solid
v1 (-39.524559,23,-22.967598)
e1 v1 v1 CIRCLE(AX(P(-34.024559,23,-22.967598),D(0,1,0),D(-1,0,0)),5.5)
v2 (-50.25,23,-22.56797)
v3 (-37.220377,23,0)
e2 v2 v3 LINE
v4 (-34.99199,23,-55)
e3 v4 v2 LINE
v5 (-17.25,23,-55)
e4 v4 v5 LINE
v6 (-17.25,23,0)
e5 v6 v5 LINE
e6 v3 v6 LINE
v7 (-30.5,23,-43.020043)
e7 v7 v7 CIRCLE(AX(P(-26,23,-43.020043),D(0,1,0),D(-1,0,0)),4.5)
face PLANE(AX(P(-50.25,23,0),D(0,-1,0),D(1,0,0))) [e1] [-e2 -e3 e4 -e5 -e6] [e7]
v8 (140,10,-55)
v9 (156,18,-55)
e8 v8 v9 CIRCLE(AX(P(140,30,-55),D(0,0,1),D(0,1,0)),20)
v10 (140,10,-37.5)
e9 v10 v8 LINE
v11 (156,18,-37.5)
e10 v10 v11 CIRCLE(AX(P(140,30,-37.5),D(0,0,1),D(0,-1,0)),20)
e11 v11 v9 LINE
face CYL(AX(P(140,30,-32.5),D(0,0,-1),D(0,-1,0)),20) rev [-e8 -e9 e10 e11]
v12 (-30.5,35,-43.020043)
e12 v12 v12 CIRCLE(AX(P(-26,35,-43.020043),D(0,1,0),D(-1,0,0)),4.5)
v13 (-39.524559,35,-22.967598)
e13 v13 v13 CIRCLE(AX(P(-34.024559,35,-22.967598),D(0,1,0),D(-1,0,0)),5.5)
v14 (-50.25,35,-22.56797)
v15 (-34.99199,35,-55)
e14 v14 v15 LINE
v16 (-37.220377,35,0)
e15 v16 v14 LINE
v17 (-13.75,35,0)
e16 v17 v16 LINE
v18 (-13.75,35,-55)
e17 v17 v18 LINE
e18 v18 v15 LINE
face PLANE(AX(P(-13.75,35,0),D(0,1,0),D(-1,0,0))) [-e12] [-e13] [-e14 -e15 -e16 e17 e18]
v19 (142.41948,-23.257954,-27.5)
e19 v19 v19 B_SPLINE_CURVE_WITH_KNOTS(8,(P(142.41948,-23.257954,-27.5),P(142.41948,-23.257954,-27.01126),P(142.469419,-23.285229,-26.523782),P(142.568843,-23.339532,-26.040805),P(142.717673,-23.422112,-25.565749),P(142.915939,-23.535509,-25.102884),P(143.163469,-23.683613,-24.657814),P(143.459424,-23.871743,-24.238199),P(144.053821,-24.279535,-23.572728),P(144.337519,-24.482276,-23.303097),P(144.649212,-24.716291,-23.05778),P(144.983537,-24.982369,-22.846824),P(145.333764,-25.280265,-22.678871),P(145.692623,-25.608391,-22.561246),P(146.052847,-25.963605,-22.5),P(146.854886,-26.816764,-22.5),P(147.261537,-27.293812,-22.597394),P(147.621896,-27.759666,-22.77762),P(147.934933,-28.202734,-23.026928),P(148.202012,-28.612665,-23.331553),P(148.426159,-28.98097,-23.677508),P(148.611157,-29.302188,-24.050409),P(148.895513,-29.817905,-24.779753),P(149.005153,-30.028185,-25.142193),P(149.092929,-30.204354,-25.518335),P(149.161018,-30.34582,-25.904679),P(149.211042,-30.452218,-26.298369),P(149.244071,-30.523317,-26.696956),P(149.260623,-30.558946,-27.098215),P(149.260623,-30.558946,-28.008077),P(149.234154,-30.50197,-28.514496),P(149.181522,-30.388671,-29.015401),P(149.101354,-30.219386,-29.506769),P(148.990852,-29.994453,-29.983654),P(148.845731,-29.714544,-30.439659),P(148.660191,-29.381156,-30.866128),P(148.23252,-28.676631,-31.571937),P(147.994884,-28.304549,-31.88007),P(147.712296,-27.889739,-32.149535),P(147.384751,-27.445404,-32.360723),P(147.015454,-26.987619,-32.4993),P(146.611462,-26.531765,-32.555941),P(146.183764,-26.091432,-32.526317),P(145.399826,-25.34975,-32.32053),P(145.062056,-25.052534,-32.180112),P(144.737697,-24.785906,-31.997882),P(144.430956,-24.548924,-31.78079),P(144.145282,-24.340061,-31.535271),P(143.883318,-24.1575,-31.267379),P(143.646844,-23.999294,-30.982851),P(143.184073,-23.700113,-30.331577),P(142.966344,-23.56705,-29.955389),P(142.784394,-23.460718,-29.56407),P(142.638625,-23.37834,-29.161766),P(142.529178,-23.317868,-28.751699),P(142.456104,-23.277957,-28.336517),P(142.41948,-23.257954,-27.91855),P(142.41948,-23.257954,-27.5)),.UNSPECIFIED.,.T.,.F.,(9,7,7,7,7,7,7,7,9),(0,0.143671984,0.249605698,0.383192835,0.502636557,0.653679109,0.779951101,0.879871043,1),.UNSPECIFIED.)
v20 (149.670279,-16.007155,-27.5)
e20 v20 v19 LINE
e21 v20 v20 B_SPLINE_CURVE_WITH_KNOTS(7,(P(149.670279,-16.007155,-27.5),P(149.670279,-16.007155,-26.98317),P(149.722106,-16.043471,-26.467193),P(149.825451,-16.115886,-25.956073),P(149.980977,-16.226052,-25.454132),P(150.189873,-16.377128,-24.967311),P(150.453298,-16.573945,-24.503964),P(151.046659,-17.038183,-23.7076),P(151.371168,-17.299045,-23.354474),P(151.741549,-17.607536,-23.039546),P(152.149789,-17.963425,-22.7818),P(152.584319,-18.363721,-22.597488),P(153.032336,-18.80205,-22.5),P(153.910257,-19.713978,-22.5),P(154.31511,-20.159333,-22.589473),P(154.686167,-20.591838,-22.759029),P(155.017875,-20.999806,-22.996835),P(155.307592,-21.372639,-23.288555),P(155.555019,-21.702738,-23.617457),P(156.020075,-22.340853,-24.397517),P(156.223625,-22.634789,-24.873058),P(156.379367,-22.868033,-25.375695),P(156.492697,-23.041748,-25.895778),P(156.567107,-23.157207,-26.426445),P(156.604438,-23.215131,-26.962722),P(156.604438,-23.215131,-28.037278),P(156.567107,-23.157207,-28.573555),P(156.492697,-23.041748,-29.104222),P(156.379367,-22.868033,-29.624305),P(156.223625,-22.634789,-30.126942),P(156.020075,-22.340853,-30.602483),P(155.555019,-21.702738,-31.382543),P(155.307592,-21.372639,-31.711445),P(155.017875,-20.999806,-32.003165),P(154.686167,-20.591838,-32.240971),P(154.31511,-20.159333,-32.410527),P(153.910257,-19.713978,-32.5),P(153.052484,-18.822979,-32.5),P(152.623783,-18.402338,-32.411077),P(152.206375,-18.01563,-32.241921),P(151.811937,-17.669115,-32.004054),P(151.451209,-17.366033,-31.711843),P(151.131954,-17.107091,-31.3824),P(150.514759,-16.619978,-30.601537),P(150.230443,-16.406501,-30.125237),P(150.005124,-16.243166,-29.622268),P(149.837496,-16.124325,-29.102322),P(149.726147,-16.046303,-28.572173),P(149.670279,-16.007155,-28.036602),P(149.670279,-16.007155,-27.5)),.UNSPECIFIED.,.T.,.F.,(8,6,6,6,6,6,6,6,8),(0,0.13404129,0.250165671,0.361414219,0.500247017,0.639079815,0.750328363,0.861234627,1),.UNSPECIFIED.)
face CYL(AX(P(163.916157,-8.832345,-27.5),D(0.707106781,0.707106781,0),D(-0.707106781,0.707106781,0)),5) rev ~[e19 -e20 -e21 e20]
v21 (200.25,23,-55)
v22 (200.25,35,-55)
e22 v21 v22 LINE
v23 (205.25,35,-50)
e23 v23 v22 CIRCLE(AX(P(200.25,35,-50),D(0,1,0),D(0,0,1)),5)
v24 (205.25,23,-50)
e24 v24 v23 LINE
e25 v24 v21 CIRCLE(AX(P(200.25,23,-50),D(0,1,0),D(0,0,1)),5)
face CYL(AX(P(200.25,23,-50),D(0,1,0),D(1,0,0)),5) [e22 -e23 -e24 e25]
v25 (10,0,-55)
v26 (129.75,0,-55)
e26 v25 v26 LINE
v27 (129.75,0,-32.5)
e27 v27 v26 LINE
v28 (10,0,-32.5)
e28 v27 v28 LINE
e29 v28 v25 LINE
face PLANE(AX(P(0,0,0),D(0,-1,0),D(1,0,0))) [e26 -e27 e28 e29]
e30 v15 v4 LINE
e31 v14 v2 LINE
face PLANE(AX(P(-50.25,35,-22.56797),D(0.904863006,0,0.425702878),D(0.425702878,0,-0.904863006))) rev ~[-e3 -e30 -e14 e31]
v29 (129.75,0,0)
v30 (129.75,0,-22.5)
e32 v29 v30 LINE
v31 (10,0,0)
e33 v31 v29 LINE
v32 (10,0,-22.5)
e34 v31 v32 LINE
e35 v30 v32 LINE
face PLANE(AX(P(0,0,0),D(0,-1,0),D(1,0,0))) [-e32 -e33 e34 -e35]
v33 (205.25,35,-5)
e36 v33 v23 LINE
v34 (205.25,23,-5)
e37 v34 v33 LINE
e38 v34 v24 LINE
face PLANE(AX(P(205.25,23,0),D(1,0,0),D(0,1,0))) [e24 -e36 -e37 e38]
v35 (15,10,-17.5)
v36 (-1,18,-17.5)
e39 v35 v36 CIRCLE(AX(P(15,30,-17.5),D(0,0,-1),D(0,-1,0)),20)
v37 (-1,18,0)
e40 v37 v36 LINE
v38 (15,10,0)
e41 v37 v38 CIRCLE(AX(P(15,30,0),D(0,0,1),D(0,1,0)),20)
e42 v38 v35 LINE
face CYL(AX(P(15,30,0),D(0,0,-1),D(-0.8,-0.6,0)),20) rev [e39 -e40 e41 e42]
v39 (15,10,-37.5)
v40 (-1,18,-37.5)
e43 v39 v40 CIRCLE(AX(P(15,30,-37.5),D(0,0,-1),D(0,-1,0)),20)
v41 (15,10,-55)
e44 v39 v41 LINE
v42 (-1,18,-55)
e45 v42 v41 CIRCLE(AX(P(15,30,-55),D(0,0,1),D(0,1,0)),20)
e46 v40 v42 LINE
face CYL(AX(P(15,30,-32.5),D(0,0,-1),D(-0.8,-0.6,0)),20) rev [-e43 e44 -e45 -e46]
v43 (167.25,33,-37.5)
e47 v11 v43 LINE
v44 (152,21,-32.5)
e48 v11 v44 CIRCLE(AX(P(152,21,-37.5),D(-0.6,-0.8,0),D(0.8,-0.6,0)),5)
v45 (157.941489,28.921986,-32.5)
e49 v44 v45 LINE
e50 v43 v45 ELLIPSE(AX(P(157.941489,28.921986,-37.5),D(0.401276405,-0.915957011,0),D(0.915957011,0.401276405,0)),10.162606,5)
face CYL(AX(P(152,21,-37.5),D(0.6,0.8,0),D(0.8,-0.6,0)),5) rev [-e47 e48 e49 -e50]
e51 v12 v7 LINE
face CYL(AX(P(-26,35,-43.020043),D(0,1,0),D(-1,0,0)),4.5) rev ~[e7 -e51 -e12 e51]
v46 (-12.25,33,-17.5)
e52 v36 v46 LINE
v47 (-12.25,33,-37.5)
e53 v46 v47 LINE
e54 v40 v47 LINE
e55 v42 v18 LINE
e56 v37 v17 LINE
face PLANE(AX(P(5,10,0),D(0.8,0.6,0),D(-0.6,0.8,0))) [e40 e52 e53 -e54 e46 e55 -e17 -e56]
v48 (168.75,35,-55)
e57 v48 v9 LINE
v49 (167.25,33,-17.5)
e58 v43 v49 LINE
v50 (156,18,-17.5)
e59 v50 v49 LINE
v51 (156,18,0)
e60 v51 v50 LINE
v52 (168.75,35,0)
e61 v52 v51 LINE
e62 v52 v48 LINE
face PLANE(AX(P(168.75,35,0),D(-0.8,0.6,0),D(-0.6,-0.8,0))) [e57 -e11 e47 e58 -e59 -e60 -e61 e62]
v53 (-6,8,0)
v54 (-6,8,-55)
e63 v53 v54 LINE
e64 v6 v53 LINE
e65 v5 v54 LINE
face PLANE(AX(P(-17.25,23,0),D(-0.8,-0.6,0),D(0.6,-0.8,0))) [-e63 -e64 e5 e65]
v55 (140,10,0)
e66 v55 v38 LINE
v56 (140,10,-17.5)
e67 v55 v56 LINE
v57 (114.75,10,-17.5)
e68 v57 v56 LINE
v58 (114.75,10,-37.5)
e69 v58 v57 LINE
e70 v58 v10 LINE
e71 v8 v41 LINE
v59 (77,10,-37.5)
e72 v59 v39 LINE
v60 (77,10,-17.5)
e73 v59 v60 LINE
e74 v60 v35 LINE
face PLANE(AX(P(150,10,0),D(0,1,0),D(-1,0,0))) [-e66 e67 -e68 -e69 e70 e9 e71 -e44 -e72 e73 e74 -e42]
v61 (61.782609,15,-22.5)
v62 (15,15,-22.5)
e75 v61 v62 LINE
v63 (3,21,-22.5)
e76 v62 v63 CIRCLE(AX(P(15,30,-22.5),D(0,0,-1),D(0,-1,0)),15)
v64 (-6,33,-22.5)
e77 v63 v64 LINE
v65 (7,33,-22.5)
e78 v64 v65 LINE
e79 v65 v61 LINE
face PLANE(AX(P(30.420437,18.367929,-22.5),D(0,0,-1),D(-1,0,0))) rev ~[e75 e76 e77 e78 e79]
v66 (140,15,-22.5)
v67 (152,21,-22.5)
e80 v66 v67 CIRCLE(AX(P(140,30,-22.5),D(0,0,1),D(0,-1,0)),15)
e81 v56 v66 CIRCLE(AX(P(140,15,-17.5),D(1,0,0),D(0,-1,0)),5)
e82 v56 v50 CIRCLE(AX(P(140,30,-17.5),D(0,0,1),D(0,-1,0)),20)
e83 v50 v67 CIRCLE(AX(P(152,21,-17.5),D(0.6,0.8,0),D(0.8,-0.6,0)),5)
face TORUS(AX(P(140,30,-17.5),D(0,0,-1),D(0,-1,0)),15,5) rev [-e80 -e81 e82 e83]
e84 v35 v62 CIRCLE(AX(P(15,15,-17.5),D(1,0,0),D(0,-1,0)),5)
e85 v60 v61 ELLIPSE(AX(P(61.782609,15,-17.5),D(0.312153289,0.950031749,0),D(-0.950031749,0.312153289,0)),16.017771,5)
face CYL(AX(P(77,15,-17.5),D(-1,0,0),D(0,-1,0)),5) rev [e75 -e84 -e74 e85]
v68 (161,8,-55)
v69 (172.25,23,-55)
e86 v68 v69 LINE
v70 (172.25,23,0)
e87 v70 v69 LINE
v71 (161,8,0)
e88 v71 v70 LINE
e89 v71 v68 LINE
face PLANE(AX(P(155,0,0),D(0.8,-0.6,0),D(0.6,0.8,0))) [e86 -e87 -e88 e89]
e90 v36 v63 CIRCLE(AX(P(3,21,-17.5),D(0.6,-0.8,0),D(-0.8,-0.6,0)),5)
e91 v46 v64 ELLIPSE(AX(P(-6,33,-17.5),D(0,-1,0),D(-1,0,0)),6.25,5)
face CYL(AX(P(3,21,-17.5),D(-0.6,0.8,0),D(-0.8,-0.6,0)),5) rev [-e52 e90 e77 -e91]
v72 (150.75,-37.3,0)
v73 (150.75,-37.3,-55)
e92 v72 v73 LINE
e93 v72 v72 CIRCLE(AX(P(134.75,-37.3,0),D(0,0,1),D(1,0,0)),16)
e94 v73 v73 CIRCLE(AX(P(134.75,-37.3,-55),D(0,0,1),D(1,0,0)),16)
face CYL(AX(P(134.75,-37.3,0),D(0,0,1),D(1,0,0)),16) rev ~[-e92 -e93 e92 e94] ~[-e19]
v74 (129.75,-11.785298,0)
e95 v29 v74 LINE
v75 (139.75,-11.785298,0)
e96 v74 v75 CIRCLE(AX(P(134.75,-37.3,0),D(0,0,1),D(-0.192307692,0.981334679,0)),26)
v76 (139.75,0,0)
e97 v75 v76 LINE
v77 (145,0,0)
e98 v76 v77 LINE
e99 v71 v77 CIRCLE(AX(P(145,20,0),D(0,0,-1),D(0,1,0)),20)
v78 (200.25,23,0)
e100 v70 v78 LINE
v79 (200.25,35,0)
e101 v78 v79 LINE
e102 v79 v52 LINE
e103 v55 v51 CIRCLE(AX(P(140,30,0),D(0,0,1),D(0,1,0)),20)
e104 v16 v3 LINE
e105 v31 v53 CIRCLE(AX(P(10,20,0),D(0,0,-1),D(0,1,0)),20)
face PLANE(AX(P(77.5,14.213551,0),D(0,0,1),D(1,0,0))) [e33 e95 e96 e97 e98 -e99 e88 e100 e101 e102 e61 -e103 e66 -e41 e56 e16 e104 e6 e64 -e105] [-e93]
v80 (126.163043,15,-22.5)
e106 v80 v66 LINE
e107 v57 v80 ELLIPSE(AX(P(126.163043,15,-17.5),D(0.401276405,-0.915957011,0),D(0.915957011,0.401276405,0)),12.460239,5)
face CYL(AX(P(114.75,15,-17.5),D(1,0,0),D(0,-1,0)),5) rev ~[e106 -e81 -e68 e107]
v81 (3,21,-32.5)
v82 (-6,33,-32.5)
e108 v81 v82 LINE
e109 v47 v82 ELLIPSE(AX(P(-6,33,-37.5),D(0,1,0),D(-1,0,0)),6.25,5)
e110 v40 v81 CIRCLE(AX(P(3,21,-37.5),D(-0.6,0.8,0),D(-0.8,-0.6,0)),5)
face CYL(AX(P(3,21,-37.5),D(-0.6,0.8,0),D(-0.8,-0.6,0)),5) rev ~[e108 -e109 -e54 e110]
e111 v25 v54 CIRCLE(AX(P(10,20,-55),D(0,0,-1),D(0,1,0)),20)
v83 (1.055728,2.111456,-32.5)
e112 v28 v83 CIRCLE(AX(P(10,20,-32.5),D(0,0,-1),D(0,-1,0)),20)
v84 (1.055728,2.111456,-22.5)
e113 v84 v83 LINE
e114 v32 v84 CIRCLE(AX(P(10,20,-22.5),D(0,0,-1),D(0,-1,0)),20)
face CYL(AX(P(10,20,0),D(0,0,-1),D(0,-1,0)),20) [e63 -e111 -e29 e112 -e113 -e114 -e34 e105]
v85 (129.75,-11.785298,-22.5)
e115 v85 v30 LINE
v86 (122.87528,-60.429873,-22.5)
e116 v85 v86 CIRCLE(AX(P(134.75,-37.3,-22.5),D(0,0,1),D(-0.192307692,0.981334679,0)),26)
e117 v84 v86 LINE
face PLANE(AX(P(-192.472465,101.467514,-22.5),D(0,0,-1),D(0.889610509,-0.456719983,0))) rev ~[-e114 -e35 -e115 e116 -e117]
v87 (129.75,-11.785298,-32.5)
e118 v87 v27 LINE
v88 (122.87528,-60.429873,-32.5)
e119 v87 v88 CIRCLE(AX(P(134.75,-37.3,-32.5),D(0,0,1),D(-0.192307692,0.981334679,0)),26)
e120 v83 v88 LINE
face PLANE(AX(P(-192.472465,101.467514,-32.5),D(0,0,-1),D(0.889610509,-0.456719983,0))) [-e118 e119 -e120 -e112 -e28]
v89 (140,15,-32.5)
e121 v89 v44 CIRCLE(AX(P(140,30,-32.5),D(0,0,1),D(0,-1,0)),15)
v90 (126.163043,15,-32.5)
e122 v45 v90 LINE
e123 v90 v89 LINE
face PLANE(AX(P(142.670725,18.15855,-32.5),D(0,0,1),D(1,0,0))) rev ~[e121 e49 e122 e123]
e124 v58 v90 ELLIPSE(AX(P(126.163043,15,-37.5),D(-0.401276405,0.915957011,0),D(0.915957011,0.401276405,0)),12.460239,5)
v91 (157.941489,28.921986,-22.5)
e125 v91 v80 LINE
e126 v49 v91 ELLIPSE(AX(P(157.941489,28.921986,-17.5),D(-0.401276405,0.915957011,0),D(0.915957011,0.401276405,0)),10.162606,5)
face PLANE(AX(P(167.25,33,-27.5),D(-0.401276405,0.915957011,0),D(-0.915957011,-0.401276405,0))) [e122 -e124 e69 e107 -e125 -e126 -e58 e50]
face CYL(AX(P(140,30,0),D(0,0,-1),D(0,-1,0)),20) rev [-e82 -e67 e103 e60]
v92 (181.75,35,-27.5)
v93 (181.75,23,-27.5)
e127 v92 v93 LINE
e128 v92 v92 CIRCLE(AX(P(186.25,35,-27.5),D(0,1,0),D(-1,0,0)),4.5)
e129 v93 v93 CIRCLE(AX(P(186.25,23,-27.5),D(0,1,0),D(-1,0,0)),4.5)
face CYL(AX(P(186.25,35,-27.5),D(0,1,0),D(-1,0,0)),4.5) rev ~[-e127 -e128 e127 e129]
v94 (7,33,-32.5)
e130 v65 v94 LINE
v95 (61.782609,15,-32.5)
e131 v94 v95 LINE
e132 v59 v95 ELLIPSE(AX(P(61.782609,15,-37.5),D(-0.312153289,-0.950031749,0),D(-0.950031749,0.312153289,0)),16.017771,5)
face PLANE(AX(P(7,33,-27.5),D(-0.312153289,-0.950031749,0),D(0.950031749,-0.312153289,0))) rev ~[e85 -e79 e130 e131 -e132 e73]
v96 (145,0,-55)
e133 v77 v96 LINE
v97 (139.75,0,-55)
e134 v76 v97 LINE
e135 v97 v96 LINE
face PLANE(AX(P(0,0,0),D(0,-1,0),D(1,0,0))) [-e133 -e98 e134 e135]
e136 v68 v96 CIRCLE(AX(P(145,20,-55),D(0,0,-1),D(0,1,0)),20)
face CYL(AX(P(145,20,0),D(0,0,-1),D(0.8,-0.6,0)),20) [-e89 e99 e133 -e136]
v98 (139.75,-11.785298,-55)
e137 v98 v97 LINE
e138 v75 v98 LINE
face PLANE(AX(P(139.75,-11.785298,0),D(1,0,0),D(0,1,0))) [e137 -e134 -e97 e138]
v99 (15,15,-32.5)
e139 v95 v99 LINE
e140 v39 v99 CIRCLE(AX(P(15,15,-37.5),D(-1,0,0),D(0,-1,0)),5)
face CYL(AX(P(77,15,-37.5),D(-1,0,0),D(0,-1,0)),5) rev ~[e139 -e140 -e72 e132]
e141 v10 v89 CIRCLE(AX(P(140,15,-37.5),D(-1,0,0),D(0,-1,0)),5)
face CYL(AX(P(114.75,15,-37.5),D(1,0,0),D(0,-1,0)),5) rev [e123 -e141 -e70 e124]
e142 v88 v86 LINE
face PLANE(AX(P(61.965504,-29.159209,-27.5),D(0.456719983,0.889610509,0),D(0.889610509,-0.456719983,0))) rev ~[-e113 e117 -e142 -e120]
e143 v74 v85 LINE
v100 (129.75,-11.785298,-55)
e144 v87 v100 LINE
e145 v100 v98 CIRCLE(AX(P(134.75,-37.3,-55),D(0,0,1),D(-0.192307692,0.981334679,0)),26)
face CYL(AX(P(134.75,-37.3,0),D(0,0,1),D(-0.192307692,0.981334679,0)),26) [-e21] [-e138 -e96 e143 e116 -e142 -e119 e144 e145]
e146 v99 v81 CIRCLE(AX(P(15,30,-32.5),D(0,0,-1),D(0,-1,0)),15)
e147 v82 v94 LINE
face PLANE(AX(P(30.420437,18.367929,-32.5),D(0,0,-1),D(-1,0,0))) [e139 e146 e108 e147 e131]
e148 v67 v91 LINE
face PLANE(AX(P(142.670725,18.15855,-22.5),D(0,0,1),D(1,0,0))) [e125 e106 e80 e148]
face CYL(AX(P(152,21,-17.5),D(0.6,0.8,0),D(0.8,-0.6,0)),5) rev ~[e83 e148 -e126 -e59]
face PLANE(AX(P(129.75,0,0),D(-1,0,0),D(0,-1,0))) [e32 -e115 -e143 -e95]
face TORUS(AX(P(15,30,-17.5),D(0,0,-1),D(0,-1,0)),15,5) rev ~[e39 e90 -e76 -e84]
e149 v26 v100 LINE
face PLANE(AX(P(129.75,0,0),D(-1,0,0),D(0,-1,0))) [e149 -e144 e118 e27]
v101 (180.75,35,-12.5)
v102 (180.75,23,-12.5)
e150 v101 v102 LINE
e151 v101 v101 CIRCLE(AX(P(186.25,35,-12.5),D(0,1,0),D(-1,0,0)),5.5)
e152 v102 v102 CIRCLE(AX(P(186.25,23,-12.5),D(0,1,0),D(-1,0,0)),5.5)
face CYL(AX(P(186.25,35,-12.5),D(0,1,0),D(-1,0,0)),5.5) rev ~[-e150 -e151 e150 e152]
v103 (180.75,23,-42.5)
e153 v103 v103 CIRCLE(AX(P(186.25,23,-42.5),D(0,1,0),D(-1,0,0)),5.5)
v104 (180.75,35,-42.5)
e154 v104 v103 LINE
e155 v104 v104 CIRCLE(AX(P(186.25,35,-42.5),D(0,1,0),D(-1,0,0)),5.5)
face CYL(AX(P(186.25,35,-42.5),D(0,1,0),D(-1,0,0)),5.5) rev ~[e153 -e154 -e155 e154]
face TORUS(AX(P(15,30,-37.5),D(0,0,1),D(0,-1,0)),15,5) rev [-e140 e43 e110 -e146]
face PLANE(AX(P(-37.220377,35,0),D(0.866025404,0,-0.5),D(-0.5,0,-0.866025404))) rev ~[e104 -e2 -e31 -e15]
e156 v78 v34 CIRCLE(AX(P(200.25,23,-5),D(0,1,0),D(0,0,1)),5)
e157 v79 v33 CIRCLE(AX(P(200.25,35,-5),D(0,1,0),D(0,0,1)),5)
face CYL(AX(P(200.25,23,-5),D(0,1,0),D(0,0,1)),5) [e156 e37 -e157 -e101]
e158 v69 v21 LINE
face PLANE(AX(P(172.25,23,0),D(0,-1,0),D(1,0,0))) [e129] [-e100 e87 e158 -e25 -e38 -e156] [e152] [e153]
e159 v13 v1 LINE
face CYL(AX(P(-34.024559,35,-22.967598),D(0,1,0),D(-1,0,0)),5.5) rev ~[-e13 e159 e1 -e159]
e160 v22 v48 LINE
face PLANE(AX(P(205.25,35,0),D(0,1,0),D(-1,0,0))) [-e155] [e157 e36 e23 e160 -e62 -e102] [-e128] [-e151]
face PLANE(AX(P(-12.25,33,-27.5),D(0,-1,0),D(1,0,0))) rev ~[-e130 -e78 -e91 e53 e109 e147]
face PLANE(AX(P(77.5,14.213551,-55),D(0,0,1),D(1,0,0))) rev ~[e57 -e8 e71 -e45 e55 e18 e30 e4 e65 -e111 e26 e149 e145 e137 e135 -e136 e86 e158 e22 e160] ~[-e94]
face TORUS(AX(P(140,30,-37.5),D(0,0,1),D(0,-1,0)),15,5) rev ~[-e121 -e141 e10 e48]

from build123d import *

# Parameters (mm, degrees)
BRACKET_BODY_DEPTH          = 55
WEB_START                   = -27.5
WEB_BOSS_180X70_DEPTH       = 5
WEB_BOSS_74_DEPTH           = 5
HUB_BOSS_SKETCH_R           = 26
HUB_BOSS_DEPTH              = 55
ANGLED_CUT_30DEG_DEPTH      = 55
BEND_FILLETS_R20_R          = 20
HUB_SUPPORT_RIB_REACH       = 218.543
SUPPORT_RIB_SKETCH_WALL_W   = 572.021051398
SUPPORT_RIB_SKETCH_WALL_H   = 10
HUB_BORE_SKETCH_R           = 16
HUB_BORE_32_DEPTH           = 55
FLANGE_HOLES_SKETCH_R       = 5.5
FLANGE_HOLES_SKETCH_R_2     = 4.5
FLANGE_MOUNTING_HOLES_DEPTH = 55
EDGE_FILLETS_R5_R           = 5
WEB_FILLETS_R5_R            = 5
CROSS_HOLE_SKETCH_R         = 5
HUB_CROSS_HOLE_10_DEPTH     = 45


with BuildPart() as part:
    # Bracket Profile Sketch → Bracket Body (new body)
    with BuildSketch(Plane.XY):
        Polygon((0, 0), (155, 0), (172.25, 23), (205.25, 23), (205.25, 35), (168.75, 35), (150, 10), (5, 10), (-13.75, 35), (-50.25, 35), (-50.25, 23), (-17.25, 23), align=None)
    extrude(amount=-BRACKET_BODY_DEPTH)

    # Web Boss 180x70 Sketch → Web Boss 180x70 (add, symmetric)
    with BuildSketch(Plane.XY.offset(WEB_START)):
        Polygon((-12.25, 33), (7, 33), (77, 10), (5, 10), align=None)
    extrude(amount=WEB_BOSS_180X70_DEPTH, both=True)

    # Web Boss 74 Sketch → Web Boss 74 (add, symmetric)
    with BuildSketch(Plane.XY.offset(WEB_START)):
        Polygon((167.25, 33), (114.75, 10), (150, 10), align=None)
    extrude(amount=WEB_BOSS_74_DEPTH, both=True)

    # Hub Boss Sketch → Hub Boss (add)
    with BuildSketch(Plane.XY):
        with Locations((134.75, -37.3)):
            Circle(HUB_BOSS_SKETCH_R)
        with BuildLine():
            ThreePointArc((129.75, -11.785298356), (134.75, -11.3), (139.75, -11.785298356))
            Line((139.75, -11.785298356), (139.75, 0))
            Line((139.75, 0), (129.75, 0))
            Line((129.75, 0), (129.75, -11.785298356))
        make_face()
    extrude(amount=-HUB_BOSS_DEPTH)

    # Angled Cut Sketch → Angled Cut 30deg (cut)
    with BuildSketch(Plane(origin=(0, 35, 0), x_dir=(1, 0, 0), z_dir=(0, 1, 0))):
        Polygon((-50.25, 55), (-50.25, 22.567969878), (-34.99199027, 55), align=None)
        Polygon((-37.220376516, 0), (-50.25, 22.567969878), (-50.25, 0), align=None)
    extrude(amount=-ANGLED_CUT_30DEG_DEPTH, mode=Mode.SUBTRACT)

    # Bend Fillets R20
    bend_fillets_r20_edges = [part.edges().sort_by_distance(p)[0] for p in [
        (5, 10, -43.75),
        (150, 10, -43.75),
        (155, 0, -27.5),
        (0, 0, -27.5),
        (5, 10, -11.25),
        (150, 10, -11.25),
    ]]
    fillet(bend_fillets_r20_edges, radius=BEND_FILLETS_R20_R)

    # Support Rib Sketch wall → Hub Support Rib (add, up to next)
    with BuildSketch(Plane(origin=(61.965504267, -29.159208524, -27.5), x_dir=(0.889610508712, -0.45671998291, 0), z_dir=(0.45671998291, 0.889610508712, 0)), mode=Mode.PRIVATE) as hub_support_rib_sk1:
        Rectangle(SUPPORT_RIB_SKETCH_WALL_W, SUPPORT_RIB_SKETCH_WALL_H)
    hub_support_rib_tool1 = extrude(hub_support_rib_sk1.sketch, amount=HUB_SUPPORT_RIB_REACH, mode=Mode.PRIVATE) - part.part
    add(hub_support_rib_tool1.solids().sort_by_distance((61.965504267, -29.159208524, -27.5))[0])

    # Hub Bore Sketch → Hub Bore Ø32 (cut)
    with BuildSketch(Plane.XY):
        with Locations((134.75, -37.3)):
            Circle(HUB_BORE_SKETCH_R)
    extrude(amount=-HUB_BORE_32_DEPTH, mode=Mode.SUBTRACT)

    # Flange Holes Sketch → Flange Mounting Holes (cut)
    with BuildSketch(Plane(origin=(0, 35, 0), x_dir=(1, 0, 0), z_dir=(0, 1, 0))):
        with Locations(Location((-34.024558742, 22.967597982, 0), (0, 0, 180))):
            Circle(FLANGE_HOLES_SKETCH_R)
        with Locations(Location((-26, 43.020043273, 0), (0, 0, 180))):
            Circle(FLANGE_HOLES_SKETCH_R_2)
        with Locations(Location((186.25, 42.5, 0), (0, 0, 180))):
            Circle(FLANGE_HOLES_SKETCH_R)
        with Locations(Location((186.25, 27.5, 0), (0, 0, 180))):
            Circle(FLANGE_HOLES_SKETCH_R_2)
        with Locations(Location((186.25, 12.5, 0), (0, 0, 180))):
            Circle(FLANGE_HOLES_SKETCH_R)
    extrude(amount=-FLANGE_MOUNTING_HOLES_DEPTH, mode=Mode.SUBTRACT)

    # Edge Fillets R5
    edge_fillets_r5_edges = [part.edges().sort_by_distance(p)[0] for p in [
        (205.25, 29, 0),
        (205.25, 29, -55),
    ]]
    fillet(edge_fillets_r5_edges, radius=EDGE_FILLETS_R5_R)

    # Web Fillets R5
    web_fillets_r5_edges = [part.edges().sort_by_distance(p)[0] for p in [
        (161.625, 25.5, -22.5),
        (161.625, 25.5, -32.5),
        (148.94427191, 12.11145618, -32.5),
        (46, 10, -32.5),
        (46, 10, -22.5),
        (148.94427191, 12.11145618, -22.5),
        (6.05572809, 12.11145618, -32.5),
        (6.05572809, 12.11145618, -22.5),
        (-6.625, 25.5, -32.5),
        (-6.625, 25.5, -22.5),
        (127.375, 10, -32.5),
        (127.375, 10, -22.5),
    ]]
    fillet(web_fillets_r5_edges, radius=WEB_FILLETS_R5_R)

    # Cross Hole Sketch → Hub Cross Hole Ø10 (cut)
    with BuildSketch(Plane(origin=(163.566905934, -8.483094066, 0), x_dir=(0.7071067811865488, -0.7071067811865462, 0), z_dir=(0.7071067811865462, 0.7071067811865488, 0))):
        with Locations(Location((0.493915353, 27.5, 0), (0, 0, 180))):
            Circle(CROSS_HOLE_SKETCH_R)
    extrude(amount=-HUB_CROSS_HOLE_10_DEPTH, mode=Mode.SUBTRACT)


solid = part.part
